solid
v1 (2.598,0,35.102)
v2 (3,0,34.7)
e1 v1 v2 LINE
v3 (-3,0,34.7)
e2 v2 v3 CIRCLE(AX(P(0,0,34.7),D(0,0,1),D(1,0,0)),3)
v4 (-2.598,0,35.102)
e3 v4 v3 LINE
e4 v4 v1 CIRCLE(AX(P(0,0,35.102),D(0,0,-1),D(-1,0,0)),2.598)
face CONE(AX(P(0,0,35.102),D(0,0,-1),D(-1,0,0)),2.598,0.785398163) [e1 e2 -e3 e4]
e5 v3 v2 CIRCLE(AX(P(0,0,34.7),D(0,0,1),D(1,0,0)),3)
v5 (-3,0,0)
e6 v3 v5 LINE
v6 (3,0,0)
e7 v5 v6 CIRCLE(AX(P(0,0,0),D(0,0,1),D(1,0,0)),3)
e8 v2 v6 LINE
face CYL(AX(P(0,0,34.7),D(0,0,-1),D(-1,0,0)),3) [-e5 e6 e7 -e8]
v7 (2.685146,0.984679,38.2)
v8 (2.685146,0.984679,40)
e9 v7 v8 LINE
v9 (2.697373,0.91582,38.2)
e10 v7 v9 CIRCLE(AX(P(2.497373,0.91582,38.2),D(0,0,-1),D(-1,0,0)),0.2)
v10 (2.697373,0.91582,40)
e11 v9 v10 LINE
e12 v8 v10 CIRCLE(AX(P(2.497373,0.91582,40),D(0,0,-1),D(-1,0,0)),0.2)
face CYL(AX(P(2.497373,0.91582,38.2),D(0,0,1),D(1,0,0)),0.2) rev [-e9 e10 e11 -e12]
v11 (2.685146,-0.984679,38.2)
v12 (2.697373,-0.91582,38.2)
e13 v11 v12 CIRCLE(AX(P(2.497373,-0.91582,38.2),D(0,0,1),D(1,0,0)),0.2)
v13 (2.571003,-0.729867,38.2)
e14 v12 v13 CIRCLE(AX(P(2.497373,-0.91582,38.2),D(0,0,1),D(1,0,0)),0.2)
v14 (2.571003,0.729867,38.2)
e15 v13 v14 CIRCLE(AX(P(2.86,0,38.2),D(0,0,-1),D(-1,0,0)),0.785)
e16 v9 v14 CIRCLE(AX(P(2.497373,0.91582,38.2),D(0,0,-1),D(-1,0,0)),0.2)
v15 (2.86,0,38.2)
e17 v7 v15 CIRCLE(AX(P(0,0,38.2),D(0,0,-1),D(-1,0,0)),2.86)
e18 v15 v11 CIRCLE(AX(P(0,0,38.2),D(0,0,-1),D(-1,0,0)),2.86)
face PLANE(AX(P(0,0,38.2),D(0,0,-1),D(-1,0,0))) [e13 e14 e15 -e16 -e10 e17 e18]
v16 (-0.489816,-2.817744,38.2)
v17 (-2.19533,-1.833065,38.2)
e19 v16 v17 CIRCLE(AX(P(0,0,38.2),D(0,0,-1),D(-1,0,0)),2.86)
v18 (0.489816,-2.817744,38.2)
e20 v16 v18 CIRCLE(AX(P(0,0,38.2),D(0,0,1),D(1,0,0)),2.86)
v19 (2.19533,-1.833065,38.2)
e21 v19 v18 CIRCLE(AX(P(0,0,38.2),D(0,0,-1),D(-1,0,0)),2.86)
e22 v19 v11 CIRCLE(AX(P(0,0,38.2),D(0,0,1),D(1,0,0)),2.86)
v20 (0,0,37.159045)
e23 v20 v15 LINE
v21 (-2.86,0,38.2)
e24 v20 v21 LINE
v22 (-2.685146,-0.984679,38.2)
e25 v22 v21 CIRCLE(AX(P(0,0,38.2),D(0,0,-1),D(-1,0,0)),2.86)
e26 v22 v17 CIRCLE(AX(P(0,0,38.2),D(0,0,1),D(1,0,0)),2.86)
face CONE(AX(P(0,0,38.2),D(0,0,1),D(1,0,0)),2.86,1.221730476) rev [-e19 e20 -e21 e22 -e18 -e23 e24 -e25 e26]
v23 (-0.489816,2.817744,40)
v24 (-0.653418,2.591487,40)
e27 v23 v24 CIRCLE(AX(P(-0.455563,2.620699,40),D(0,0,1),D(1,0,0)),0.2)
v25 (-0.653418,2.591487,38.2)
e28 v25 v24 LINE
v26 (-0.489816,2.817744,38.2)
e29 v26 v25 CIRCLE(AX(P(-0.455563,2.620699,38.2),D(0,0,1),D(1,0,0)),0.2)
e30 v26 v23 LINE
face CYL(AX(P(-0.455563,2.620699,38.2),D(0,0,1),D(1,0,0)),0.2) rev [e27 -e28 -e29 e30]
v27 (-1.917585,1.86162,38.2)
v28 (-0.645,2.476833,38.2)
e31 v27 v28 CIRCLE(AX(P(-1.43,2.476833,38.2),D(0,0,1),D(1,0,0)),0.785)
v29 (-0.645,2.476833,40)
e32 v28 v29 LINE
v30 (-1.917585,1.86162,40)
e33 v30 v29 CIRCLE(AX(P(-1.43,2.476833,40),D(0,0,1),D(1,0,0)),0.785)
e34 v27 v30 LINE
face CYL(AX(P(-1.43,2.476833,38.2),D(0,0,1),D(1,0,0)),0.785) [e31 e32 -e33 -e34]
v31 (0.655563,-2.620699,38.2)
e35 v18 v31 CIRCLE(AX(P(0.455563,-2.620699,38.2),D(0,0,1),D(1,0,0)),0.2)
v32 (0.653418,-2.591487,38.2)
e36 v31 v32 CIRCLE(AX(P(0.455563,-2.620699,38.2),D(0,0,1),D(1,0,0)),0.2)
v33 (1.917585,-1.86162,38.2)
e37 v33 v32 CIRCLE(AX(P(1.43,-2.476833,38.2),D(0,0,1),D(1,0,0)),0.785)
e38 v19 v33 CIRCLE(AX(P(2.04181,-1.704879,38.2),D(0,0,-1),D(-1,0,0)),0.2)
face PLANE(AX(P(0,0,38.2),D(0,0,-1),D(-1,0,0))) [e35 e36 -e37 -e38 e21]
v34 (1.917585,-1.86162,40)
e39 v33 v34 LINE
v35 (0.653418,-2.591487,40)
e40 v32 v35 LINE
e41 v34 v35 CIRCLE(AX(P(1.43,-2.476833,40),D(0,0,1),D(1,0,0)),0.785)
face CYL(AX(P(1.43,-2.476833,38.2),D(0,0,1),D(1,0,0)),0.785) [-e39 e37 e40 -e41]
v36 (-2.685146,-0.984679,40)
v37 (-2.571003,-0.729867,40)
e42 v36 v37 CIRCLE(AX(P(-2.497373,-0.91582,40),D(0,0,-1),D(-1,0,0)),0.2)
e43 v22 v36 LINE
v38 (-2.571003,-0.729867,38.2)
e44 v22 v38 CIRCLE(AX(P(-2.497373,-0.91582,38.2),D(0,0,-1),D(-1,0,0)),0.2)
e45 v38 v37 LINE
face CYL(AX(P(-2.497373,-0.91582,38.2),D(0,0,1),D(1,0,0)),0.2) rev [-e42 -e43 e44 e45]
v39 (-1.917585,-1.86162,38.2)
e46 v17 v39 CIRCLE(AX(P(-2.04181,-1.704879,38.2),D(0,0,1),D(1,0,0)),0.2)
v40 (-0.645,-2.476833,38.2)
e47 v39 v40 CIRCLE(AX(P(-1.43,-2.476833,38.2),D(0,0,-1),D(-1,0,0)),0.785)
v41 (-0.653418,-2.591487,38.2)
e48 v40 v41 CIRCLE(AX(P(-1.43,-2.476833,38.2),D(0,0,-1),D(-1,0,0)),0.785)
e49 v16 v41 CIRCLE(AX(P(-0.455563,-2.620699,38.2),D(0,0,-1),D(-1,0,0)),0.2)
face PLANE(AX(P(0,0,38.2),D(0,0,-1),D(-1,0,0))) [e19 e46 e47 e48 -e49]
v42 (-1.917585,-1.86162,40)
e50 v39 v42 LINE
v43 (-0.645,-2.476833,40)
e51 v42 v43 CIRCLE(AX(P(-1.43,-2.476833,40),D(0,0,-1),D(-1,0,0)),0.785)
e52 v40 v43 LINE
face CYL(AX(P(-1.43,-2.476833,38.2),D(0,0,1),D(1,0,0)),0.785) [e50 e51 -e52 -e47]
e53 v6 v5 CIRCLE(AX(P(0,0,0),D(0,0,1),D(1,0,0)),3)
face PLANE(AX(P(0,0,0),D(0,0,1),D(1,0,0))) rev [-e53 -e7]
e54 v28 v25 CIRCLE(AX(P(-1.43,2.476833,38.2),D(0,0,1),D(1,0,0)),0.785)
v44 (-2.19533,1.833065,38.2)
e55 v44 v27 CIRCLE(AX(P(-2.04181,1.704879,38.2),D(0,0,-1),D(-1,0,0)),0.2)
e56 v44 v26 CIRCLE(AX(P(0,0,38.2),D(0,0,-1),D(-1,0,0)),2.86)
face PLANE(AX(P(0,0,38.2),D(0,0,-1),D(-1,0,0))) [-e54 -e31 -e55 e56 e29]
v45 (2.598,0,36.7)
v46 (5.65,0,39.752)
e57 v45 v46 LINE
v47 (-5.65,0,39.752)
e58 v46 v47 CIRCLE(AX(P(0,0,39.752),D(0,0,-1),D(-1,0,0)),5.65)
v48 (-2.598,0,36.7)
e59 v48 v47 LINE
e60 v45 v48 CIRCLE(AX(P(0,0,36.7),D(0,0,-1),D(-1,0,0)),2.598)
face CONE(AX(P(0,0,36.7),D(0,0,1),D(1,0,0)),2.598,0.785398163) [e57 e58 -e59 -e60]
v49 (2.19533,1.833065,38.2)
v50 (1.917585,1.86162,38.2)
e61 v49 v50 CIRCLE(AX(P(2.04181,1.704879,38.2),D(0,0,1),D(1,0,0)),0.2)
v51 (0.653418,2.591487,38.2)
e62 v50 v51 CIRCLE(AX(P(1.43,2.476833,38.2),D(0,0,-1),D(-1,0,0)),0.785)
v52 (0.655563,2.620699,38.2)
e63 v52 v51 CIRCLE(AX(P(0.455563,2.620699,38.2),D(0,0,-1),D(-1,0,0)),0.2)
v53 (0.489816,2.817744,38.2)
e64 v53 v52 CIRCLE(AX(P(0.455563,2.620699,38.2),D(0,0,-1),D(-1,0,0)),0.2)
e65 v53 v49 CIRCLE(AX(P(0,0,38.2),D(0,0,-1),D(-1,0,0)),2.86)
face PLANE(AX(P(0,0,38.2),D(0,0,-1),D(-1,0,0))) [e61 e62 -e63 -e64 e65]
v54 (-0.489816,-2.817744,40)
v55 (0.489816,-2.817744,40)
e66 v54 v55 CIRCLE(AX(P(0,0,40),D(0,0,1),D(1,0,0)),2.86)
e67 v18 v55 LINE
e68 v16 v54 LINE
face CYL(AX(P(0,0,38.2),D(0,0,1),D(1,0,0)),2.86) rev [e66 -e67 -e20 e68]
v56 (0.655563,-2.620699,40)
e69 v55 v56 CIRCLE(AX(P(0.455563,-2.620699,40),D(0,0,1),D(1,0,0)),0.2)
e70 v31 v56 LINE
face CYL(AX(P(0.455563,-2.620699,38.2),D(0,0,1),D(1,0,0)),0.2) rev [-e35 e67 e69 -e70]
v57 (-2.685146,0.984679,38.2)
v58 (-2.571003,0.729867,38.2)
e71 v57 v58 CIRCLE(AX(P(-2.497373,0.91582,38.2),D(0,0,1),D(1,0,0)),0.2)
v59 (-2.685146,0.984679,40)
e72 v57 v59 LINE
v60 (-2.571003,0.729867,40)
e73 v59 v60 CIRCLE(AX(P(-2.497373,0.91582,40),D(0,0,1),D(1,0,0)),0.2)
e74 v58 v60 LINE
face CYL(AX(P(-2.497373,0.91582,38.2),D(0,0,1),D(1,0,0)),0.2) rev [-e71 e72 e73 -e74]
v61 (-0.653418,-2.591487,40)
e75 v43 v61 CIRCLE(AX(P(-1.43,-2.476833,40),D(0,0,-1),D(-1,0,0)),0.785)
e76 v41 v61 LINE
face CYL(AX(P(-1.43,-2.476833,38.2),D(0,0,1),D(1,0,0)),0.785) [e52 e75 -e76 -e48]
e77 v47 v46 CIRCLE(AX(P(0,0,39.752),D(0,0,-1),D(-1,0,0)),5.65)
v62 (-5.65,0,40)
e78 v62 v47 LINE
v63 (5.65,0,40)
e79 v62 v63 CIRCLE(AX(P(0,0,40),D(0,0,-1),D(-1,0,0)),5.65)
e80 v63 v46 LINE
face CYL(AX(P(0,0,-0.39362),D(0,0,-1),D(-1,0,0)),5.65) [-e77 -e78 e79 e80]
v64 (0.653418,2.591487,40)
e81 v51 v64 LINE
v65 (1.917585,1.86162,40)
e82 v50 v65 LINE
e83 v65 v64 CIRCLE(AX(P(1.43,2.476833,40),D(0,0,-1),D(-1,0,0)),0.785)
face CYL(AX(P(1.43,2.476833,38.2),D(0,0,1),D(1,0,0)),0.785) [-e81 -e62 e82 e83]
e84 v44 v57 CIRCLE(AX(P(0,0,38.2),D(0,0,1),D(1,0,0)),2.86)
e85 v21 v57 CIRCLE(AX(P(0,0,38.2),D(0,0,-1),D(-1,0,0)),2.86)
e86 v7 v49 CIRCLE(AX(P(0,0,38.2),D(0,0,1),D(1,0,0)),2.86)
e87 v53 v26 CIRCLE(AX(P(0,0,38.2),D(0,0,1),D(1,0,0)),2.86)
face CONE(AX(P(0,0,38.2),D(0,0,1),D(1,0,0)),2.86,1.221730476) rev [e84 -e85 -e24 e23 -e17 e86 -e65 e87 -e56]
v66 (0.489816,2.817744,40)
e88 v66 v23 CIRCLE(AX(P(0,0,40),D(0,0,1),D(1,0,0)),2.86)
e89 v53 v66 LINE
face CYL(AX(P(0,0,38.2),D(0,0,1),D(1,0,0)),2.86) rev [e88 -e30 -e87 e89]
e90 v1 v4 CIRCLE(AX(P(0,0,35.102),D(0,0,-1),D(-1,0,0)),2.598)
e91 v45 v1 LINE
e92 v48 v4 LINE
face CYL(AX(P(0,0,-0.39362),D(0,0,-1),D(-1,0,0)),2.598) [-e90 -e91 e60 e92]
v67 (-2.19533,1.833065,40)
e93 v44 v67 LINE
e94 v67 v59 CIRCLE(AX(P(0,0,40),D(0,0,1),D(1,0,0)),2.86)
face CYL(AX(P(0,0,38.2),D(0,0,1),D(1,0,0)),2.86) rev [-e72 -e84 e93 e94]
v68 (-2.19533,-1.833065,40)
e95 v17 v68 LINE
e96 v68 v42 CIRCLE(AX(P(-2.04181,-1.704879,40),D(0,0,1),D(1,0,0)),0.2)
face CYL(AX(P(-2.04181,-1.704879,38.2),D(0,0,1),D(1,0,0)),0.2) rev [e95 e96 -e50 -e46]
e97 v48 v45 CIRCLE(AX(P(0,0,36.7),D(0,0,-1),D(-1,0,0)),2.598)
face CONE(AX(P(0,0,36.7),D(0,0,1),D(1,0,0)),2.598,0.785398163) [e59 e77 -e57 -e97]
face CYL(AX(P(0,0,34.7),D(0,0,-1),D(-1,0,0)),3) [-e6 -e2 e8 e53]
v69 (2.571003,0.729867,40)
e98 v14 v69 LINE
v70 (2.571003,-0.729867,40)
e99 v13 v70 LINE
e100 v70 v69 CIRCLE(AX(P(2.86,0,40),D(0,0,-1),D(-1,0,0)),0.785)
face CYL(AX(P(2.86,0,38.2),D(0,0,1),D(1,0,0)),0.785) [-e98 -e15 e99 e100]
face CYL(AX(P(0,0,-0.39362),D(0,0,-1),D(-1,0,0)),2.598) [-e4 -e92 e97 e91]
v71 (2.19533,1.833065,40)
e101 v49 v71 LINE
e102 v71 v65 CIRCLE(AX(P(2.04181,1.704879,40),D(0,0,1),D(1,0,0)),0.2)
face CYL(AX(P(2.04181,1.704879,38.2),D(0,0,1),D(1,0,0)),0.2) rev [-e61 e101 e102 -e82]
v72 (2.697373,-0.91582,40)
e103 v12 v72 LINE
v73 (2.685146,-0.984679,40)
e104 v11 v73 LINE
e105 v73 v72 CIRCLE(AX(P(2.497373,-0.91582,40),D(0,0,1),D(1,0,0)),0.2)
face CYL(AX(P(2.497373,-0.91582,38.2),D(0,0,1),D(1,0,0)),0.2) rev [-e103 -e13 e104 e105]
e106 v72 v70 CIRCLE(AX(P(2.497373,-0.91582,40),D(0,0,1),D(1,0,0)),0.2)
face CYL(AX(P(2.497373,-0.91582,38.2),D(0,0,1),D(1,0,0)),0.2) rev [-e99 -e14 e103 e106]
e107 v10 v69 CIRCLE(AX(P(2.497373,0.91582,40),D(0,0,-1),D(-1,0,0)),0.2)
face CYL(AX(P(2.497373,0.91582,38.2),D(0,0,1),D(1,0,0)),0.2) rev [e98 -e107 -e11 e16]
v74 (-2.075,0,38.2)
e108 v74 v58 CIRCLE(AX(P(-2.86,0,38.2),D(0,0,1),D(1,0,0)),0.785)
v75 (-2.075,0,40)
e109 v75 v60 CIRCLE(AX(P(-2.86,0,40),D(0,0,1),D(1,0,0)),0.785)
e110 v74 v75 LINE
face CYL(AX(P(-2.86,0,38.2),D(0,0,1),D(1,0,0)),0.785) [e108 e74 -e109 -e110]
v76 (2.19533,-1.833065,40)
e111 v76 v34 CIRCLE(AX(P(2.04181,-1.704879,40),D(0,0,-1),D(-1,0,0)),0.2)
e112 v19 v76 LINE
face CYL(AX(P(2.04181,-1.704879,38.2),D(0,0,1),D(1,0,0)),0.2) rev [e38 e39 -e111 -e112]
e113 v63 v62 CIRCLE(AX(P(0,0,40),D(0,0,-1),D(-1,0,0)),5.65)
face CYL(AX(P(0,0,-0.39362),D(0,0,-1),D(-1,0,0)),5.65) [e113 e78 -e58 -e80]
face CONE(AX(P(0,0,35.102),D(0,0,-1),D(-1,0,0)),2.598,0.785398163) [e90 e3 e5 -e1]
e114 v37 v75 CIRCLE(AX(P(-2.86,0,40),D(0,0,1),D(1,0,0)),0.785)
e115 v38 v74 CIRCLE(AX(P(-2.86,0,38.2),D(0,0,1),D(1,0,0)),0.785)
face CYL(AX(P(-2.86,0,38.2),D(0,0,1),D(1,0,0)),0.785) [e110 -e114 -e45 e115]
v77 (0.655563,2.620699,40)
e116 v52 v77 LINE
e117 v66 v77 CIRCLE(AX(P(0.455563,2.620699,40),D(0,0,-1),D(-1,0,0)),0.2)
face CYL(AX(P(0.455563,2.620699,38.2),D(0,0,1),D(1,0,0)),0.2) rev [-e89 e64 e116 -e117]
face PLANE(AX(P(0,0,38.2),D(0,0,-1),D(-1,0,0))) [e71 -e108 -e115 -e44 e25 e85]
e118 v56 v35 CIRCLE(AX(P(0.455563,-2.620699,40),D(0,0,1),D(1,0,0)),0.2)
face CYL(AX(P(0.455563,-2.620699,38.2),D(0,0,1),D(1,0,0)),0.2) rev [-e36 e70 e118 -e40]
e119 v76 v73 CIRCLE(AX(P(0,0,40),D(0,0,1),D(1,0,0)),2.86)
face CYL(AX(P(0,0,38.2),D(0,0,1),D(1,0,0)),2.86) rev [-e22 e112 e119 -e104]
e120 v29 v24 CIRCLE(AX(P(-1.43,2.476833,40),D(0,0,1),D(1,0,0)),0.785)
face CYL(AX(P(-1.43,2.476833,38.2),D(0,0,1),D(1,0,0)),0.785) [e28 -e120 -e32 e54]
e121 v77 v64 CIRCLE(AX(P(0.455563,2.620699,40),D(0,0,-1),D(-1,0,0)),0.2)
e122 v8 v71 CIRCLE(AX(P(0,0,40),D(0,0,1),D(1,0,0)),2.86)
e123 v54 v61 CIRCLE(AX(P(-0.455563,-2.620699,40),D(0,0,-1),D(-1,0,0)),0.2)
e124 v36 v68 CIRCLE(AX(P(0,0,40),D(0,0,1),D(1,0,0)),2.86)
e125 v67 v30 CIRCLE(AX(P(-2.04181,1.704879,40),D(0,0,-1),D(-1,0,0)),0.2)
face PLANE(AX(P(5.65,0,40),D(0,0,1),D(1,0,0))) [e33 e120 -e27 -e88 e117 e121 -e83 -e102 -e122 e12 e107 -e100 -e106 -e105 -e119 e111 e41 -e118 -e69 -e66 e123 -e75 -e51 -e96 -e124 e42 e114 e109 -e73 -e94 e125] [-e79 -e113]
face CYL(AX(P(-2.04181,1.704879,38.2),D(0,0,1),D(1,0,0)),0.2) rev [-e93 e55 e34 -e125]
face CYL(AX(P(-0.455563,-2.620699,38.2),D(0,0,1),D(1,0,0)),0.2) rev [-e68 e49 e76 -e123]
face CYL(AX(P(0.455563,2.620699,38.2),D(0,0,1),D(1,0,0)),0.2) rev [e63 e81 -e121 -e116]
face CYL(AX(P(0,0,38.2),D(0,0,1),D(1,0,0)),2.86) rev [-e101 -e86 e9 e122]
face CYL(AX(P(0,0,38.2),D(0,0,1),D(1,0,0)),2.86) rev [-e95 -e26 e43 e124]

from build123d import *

# Parameters (mm, degrees)
SKETCH1_R          = 3
BASE_EXTRUDE_DEPTH = 34.7
CUT_EXTRUDE1_DEPTH = 1.8


with BuildPart() as part:
    # Sketch1 → Base-Extrude (new body)
    with BuildSketch(Plane.XY):
        Circle(SKETCH1_R)
    extrude(amount=BASE_EXTRUDE_DEPTH)

    # Sketch6 → Base-Revolve2 (revolve)
    with BuildSketch(Plane(origin=(0, 0, 0), x_dir=(1, 0, 0), z_dir=(0, 1, 0)), mode=Mode.PRIVATE) as base_revolve2_sk:
        Polygon((2.598, -36.7), (5.65, -39.752), (5.65, -40), (0, -40), (0, -34.7), (3, -34.7), (2.598, -35.102), align=None)
    revolve(base_revolve2_sk.sketch.rotate(Axis((0, 0, -0.393620135), (0, 0, 1)), 180), axis=Axis((0, 0, -0.393620135), (0, 0, 1)))

    # Sketch7 → Cut-Extrude1 (cut)
    with BuildSketch(Plane.XY.offset(40)):
        with BuildLine():
            ThreePointArc((0.489815827, 2.817743859), (0, 2.86), (-0.489815827, 2.817743859))
            ThreePointArc((-0.489815827, 2.817743859), (-0.617632508, 2.737888703), (-0.653418206, 2.591487427))
            ThreePointArc((-0.653418206, 2.591487427), (-1.0375, 1.797002713), (-1.917584843, 1.861620479))
            ThreePointArc((-1.917584843, 1.861620479), (-2.062264916, 1.903829794), (-2.19532985, 1.833064879))
            ThreePointArc((-2.19532985, 1.833064879), (-2.476832655, 1.43), (-2.685145677, 0.984678981))
            ThreePointArc((-2.685145677, 0.984678981), (-2.679897424, 0.83405891), (-2.571003048, 0.729866948))
            ThreePointArc((-2.571003048, 0.729866948), (-2.075, 0), (-2.571003048, -0.729866948))
            ThreePointArc((-2.571003048, -0.729866948), (-2.679897424, -0.83405891), (-2.685145677, -0.984678981))
            ThreePointArc((-2.685145677, -0.984678981), (-2.476832655, -1.43), (-2.19532985, -1.833064879))
            ThreePointArc((-2.19532985, -1.833064879), (-2.062264916, -1.903829794), (-1.917584843, -1.861620479))
            ThreePointArc((-1.917584843, -1.861620479), (-1.0375, -1.797002713), (-0.653418206, -2.591487427))
            ThreePointArc((-0.653418206, -2.591487427), (-0.617632508, -2.737888703), (-0.489815827, -2.817743859))
            ThreePointArc((-0.489815827, -2.817743859), (0, -2.86), (0.489815827, -2.817743859))
            ThreePointArc((0.489815827, -2.817743859), (0.617632508, -2.737888703), (0.653418206, -2.591487427))
            ThreePointArc((0.653418206, -2.591487427), (1.0375, -1.797002713), (1.917584843, -1.861620479))
            ThreePointArc((1.917584843, -1.861620479), (2.062264916, -1.903829794), (2.19532985, -1.833064879))
            ThreePointArc((2.19532985, -1.833064879), (2.476832655, -1.43), (2.685145677, -0.984678981))
            ThreePointArc((2.685145677, -0.984678981), (2.679897424, -0.83405891), (2.571003048, -0.729866948))
            ThreePointArc((2.571003048, -0.729866948), (2.075, 0), (2.571003048, 0.729866948))
            ThreePointArc((2.571003048, 0.729866948), (2.679897424, 0.83405891), (2.685145677, 0.984678981))
            ThreePointArc((2.685145677, 0.984678981), (2.476832655, 1.43), (2.19532985, 1.833064879))
            ThreePointArc((2.19532985, 1.833064879), (2.062264916, 1.903829794), (1.917584843, 1.861620479))
            ThreePointArc((1.917584843, 1.861620479), (1.0375, 1.797002713), (0.653418206, 2.591487427))
            ThreePointArc((0.653418206, 2.591487427), (0.617632508, 2.737888703), (0.489815827, 2.817743859))
        make_face()
    extrude(amount=-CUT_EXTRUDE1_DEPTH, mode=Mode.SUBTRACT)

    # Sketch8 → 切除－旋转1 (revolve, cut)
    with BuildSketch(Plane(origin=(0, 0, 0), x_dir=(1, 0, 0), z_dir=(0, 1, 0))):
        Polygon((0, -38.2), (2.86, -38.2), (0, -37.15904513), align=None)
    revolve(axis=Axis((0, 0, 0), (0, 0, 1)), mode=Mode.SUBTRACT)


solid = part.part
